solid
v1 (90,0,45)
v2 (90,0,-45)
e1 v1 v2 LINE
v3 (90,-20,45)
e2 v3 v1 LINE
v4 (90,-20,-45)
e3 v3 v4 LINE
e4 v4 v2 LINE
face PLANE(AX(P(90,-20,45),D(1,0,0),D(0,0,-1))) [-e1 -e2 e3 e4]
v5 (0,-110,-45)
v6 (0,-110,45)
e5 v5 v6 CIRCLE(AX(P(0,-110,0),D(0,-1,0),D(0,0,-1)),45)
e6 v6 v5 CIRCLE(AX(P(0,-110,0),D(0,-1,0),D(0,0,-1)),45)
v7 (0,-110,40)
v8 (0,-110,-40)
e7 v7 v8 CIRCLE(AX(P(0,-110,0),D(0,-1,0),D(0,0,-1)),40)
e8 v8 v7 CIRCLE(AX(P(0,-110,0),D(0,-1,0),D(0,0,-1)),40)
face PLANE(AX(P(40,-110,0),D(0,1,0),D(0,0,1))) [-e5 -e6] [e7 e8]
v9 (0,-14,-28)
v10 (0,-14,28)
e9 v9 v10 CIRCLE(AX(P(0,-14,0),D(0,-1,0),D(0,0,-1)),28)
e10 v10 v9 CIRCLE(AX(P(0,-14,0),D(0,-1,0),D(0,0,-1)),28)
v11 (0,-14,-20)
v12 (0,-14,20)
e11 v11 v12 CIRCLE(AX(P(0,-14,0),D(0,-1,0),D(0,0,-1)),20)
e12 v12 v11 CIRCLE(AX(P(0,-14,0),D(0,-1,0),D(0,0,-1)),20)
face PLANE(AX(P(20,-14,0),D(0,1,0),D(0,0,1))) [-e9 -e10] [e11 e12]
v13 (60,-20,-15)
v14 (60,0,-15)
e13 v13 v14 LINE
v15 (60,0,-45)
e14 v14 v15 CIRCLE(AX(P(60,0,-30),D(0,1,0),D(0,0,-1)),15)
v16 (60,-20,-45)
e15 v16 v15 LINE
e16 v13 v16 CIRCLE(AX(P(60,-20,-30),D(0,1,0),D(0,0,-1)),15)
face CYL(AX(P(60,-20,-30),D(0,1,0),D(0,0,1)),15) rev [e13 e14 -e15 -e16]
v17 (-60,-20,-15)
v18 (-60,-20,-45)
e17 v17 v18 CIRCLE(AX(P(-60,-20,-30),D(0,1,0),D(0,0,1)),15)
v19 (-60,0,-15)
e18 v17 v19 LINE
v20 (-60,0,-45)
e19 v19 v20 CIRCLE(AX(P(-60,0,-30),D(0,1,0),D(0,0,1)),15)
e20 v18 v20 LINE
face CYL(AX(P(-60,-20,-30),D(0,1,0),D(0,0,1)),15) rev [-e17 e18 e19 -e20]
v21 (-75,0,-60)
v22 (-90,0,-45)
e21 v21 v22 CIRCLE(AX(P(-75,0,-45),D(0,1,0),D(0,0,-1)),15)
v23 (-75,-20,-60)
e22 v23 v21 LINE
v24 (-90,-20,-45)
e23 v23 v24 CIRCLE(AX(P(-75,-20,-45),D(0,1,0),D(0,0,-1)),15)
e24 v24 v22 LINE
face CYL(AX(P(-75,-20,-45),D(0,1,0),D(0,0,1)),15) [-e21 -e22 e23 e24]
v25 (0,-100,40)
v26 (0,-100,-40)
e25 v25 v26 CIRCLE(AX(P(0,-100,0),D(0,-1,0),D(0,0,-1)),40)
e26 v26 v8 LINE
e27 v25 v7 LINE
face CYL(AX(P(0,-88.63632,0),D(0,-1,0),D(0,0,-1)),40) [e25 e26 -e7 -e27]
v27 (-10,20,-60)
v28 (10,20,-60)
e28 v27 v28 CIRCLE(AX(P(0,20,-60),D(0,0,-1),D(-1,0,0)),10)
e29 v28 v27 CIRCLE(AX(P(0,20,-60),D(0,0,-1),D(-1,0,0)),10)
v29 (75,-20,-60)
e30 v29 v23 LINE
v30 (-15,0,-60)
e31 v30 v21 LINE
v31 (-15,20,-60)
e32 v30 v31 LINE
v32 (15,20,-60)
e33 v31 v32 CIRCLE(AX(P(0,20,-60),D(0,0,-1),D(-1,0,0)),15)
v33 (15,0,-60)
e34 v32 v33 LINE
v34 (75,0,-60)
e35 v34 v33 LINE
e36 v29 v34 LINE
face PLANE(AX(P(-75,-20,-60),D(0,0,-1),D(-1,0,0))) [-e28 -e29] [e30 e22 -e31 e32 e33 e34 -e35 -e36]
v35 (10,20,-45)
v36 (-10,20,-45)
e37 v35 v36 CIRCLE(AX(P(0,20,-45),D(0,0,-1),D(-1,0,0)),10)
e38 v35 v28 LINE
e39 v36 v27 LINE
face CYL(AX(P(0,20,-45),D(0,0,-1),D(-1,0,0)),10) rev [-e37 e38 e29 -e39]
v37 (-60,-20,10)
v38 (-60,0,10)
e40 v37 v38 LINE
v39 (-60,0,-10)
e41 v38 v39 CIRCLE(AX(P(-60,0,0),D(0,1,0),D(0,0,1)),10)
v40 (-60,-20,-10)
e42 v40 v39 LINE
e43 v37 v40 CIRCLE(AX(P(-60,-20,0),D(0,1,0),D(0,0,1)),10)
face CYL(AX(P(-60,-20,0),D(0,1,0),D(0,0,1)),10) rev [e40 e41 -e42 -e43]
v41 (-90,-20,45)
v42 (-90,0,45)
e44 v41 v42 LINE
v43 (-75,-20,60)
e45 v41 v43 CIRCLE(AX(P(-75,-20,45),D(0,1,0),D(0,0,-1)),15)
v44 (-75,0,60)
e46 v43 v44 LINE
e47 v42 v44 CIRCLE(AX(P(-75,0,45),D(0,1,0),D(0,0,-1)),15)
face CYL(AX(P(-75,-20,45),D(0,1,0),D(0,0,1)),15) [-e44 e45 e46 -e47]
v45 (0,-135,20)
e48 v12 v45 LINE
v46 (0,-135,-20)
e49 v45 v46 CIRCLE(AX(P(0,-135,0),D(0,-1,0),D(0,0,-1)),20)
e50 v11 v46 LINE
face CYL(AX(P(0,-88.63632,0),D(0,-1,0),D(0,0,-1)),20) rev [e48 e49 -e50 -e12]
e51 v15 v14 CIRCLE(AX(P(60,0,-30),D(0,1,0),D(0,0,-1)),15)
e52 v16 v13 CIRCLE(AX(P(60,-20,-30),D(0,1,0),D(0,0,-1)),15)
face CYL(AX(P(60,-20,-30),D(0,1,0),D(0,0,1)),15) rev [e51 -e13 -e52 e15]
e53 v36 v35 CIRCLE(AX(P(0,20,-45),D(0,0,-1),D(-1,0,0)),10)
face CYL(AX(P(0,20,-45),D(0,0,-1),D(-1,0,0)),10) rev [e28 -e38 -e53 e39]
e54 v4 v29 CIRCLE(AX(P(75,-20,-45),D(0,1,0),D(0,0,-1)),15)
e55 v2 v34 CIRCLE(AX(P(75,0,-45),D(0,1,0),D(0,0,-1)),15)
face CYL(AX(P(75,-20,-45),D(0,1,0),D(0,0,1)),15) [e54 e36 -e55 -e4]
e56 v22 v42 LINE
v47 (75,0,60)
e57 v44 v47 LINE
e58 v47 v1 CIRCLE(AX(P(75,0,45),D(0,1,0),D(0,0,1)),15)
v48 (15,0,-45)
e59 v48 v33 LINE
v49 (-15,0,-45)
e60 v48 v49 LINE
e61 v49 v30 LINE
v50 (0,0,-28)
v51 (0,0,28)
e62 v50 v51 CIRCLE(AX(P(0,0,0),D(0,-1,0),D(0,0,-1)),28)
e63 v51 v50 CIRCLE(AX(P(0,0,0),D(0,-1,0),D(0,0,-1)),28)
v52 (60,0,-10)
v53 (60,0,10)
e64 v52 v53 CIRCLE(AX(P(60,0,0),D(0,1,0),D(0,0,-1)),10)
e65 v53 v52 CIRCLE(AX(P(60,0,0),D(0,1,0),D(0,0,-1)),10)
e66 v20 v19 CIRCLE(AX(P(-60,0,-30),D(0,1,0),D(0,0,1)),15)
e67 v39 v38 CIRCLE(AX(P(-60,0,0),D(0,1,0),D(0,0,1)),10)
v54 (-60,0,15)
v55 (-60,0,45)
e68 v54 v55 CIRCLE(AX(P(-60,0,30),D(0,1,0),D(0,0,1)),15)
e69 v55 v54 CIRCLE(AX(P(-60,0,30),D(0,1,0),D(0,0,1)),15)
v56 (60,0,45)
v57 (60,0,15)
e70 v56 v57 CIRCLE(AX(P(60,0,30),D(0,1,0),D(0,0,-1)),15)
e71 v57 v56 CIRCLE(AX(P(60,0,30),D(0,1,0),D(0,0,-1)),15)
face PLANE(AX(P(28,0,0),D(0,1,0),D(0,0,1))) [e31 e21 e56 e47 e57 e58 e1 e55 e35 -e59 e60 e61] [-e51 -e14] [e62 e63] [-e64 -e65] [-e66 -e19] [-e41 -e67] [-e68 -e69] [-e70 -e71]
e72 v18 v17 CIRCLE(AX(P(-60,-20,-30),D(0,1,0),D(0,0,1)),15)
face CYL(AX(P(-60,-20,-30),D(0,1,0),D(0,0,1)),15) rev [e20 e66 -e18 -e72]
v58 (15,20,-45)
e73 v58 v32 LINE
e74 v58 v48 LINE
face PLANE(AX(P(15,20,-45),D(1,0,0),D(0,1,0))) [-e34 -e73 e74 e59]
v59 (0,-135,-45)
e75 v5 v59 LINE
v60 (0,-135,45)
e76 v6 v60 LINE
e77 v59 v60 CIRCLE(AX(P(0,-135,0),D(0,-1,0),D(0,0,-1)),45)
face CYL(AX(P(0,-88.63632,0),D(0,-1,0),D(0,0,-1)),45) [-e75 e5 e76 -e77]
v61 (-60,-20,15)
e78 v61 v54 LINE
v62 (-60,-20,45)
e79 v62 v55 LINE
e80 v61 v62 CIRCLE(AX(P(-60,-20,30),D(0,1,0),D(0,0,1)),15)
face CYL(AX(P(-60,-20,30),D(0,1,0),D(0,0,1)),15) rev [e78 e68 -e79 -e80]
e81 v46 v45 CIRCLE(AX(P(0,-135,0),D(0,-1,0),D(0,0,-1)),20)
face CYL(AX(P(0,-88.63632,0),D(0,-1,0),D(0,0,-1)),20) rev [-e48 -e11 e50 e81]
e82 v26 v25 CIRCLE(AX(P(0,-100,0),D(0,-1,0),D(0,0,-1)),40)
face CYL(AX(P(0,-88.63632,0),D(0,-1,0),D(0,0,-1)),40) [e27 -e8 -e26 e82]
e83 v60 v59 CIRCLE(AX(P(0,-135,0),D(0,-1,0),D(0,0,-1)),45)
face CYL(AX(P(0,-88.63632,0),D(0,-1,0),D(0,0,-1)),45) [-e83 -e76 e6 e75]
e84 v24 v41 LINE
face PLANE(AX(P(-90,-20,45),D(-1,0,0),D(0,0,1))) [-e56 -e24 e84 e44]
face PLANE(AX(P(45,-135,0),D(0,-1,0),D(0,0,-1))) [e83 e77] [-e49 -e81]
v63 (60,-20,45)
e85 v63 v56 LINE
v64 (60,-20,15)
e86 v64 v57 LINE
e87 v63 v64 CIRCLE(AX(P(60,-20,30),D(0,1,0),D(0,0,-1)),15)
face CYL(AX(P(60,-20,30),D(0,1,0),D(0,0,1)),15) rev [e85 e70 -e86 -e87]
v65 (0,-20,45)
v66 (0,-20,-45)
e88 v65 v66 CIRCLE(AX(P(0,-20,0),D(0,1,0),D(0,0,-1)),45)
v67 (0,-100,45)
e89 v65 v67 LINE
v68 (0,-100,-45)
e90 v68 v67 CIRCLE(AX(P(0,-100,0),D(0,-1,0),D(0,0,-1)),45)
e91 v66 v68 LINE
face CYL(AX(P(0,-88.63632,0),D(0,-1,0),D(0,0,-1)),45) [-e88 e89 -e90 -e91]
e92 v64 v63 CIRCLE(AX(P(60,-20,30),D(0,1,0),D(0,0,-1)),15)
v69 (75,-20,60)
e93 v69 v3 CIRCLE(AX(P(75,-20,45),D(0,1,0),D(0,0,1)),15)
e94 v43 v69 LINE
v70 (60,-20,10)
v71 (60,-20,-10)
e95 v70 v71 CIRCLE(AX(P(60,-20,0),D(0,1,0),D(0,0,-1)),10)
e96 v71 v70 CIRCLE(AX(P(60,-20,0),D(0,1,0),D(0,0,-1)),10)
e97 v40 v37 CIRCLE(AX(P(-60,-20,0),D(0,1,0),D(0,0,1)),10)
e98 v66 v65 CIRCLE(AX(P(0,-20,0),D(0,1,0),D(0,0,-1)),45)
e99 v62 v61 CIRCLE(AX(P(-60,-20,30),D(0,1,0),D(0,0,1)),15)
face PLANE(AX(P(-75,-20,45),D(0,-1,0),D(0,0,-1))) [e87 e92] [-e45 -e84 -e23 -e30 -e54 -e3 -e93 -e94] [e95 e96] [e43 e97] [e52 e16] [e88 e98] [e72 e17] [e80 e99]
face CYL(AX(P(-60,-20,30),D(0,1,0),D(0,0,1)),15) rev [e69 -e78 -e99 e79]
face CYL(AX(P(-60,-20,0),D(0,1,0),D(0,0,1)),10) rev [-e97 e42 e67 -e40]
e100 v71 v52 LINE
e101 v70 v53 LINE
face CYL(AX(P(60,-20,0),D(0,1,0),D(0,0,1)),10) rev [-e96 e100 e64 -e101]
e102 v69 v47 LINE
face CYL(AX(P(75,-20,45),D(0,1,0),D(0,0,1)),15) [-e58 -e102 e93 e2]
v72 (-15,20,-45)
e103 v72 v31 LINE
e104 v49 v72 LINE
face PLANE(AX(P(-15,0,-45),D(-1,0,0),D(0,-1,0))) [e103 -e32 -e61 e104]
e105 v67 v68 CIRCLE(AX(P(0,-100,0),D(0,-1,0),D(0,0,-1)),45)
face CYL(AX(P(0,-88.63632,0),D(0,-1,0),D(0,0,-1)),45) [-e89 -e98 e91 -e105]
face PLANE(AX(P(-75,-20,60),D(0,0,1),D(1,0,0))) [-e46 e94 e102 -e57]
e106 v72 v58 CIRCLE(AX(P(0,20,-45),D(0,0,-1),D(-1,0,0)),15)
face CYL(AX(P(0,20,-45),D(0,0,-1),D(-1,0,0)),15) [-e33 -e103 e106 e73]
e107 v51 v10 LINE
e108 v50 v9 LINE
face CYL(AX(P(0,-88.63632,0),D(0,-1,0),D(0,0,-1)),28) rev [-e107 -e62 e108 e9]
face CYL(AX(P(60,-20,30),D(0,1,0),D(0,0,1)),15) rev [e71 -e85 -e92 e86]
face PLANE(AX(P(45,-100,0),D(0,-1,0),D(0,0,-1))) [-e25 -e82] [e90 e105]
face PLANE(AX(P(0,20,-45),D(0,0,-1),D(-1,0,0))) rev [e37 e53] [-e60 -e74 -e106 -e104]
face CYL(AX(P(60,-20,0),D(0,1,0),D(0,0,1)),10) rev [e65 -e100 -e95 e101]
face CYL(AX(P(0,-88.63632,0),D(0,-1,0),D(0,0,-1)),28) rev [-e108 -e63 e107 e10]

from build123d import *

# Parameters (mm, degrees)
FLANGE_START               = -20
FLANGE_PLATE_SKETCH_R      = 15
FLANGE_PLATE_SKETCH_R_2    = 10
FLANGE_PLATE_SKETCH_R_3    = 45
FLANGE_PLATE_120X180_DEPTH = 20
EYELET_LUG_SKETCH_R        = 10
EYELET_LUG_DEPTH           = 15


with BuildPart() as part:
    # Bushing Profile Sketch → Bushing Body (revolve)
    with BuildSketch(Plane.XY, mode=Mode.PRIVATE) as bushing_body_sk:
        Polygon((45, 0), (45, -100), (40, -100), (40, -110), (45, -110), (45, -135), (20, -135), (20, -14), (28, -14), (28, 0), align=None)
    revolve(bushing_body_sk.sketch.rotate(Axis((0, -88.636319954, 0), (0, 1, 0)), 90), axis=Axis((0, -88.636319954, 0), (0, 1, 0)))

    # Flange Plate Sketch → Flange Plate 120x180 (add)
    with BuildSketch(Plane(origin=(0, 0, 0), x_dir=(1, 0, 0), z_dir=(0, 1, 0)).offset(FLANGE_START)):
        with BuildLine():
            Line((-75, -60), (75, -60))
            ThreePointArc((75, -60), (85.606601718, -55.606601718), (90, -45))
            Line((90, -45), (90, 45))
            ThreePointArc((90, 45), (85.606601718, 55.606601718), (75, 60))
            Line((75, 60), (-75, 60))
            ThreePointArc((-75, 60), (-85.606601718, 55.606601718), (-90, 45))
            Line((-90, 45), (-90, -45))
            ThreePointArc((-90, -45), (-85.606601718, -55.606601718), (-75, -60))
        make_face()
        with Locations(Location((-60, -30, 0), (0, 0, 270))):
            Circle(FLANGE_PLATE_SKETCH_R, mode=Mode.SUBTRACT)
        with Locations(Location((-60, 0, 0), (0, 0, 270))):
            Circle(FLANGE_PLATE_SKETCH_R_2, mode=Mode.SUBTRACT)
        with Locations(Location((-60, 30, 0), (0, 0, 270))):
            Circle(FLANGE_PLATE_SKETCH_R, mode=Mode.SUBTRACT)
        with Locations(Location((60, -30, 0), (0, 0, 90))):
            Circle(FLANGE_PLATE_SKETCH_R, mode=Mode.SUBTRACT)
        with Locations(Location((60, 0, 0), (0, 0, 90))):
            Circle(FLANGE_PLATE_SKETCH_R_2, mode=Mode.SUBTRACT)
        with Locations(Location((60, 30, 0), (0, 0, 90))):
            Circle(FLANGE_PLATE_SKETCH_R, mode=Mode.SUBTRACT)
        with Locations(Location((0, 0, 0), (0, 0, 90))):
            Circle(FLANGE_PLATE_SKETCH_R_3, mode=Mode.SUBTRACT)
    extrude(amount=FLANGE_PLATE_120X180_DEPTH)

    # Eyelet Lug Sketch → Eyelet Lug (add)
    with BuildSketch(Plane(origin=(0, 0, -60), x_dir=(-1, 0, 0), z_dir=(0, 0, -1))):
        with BuildLine():
            Line((-15, 20), (-15, 0))
            Line((-15, 0), (15, 0))
            Line((15, 0), (15, 20))
            ThreePointArc((15, 20), (0, 35), (-15, 20))
        make_face()
        with Locations((0, 20)):
            Circle(EYELET_LUG_SKETCH_R, mode=Mode.SUBTRACT)
    extrude(amount=-EYELET_LUG_DEPTH)


solid = part.part
